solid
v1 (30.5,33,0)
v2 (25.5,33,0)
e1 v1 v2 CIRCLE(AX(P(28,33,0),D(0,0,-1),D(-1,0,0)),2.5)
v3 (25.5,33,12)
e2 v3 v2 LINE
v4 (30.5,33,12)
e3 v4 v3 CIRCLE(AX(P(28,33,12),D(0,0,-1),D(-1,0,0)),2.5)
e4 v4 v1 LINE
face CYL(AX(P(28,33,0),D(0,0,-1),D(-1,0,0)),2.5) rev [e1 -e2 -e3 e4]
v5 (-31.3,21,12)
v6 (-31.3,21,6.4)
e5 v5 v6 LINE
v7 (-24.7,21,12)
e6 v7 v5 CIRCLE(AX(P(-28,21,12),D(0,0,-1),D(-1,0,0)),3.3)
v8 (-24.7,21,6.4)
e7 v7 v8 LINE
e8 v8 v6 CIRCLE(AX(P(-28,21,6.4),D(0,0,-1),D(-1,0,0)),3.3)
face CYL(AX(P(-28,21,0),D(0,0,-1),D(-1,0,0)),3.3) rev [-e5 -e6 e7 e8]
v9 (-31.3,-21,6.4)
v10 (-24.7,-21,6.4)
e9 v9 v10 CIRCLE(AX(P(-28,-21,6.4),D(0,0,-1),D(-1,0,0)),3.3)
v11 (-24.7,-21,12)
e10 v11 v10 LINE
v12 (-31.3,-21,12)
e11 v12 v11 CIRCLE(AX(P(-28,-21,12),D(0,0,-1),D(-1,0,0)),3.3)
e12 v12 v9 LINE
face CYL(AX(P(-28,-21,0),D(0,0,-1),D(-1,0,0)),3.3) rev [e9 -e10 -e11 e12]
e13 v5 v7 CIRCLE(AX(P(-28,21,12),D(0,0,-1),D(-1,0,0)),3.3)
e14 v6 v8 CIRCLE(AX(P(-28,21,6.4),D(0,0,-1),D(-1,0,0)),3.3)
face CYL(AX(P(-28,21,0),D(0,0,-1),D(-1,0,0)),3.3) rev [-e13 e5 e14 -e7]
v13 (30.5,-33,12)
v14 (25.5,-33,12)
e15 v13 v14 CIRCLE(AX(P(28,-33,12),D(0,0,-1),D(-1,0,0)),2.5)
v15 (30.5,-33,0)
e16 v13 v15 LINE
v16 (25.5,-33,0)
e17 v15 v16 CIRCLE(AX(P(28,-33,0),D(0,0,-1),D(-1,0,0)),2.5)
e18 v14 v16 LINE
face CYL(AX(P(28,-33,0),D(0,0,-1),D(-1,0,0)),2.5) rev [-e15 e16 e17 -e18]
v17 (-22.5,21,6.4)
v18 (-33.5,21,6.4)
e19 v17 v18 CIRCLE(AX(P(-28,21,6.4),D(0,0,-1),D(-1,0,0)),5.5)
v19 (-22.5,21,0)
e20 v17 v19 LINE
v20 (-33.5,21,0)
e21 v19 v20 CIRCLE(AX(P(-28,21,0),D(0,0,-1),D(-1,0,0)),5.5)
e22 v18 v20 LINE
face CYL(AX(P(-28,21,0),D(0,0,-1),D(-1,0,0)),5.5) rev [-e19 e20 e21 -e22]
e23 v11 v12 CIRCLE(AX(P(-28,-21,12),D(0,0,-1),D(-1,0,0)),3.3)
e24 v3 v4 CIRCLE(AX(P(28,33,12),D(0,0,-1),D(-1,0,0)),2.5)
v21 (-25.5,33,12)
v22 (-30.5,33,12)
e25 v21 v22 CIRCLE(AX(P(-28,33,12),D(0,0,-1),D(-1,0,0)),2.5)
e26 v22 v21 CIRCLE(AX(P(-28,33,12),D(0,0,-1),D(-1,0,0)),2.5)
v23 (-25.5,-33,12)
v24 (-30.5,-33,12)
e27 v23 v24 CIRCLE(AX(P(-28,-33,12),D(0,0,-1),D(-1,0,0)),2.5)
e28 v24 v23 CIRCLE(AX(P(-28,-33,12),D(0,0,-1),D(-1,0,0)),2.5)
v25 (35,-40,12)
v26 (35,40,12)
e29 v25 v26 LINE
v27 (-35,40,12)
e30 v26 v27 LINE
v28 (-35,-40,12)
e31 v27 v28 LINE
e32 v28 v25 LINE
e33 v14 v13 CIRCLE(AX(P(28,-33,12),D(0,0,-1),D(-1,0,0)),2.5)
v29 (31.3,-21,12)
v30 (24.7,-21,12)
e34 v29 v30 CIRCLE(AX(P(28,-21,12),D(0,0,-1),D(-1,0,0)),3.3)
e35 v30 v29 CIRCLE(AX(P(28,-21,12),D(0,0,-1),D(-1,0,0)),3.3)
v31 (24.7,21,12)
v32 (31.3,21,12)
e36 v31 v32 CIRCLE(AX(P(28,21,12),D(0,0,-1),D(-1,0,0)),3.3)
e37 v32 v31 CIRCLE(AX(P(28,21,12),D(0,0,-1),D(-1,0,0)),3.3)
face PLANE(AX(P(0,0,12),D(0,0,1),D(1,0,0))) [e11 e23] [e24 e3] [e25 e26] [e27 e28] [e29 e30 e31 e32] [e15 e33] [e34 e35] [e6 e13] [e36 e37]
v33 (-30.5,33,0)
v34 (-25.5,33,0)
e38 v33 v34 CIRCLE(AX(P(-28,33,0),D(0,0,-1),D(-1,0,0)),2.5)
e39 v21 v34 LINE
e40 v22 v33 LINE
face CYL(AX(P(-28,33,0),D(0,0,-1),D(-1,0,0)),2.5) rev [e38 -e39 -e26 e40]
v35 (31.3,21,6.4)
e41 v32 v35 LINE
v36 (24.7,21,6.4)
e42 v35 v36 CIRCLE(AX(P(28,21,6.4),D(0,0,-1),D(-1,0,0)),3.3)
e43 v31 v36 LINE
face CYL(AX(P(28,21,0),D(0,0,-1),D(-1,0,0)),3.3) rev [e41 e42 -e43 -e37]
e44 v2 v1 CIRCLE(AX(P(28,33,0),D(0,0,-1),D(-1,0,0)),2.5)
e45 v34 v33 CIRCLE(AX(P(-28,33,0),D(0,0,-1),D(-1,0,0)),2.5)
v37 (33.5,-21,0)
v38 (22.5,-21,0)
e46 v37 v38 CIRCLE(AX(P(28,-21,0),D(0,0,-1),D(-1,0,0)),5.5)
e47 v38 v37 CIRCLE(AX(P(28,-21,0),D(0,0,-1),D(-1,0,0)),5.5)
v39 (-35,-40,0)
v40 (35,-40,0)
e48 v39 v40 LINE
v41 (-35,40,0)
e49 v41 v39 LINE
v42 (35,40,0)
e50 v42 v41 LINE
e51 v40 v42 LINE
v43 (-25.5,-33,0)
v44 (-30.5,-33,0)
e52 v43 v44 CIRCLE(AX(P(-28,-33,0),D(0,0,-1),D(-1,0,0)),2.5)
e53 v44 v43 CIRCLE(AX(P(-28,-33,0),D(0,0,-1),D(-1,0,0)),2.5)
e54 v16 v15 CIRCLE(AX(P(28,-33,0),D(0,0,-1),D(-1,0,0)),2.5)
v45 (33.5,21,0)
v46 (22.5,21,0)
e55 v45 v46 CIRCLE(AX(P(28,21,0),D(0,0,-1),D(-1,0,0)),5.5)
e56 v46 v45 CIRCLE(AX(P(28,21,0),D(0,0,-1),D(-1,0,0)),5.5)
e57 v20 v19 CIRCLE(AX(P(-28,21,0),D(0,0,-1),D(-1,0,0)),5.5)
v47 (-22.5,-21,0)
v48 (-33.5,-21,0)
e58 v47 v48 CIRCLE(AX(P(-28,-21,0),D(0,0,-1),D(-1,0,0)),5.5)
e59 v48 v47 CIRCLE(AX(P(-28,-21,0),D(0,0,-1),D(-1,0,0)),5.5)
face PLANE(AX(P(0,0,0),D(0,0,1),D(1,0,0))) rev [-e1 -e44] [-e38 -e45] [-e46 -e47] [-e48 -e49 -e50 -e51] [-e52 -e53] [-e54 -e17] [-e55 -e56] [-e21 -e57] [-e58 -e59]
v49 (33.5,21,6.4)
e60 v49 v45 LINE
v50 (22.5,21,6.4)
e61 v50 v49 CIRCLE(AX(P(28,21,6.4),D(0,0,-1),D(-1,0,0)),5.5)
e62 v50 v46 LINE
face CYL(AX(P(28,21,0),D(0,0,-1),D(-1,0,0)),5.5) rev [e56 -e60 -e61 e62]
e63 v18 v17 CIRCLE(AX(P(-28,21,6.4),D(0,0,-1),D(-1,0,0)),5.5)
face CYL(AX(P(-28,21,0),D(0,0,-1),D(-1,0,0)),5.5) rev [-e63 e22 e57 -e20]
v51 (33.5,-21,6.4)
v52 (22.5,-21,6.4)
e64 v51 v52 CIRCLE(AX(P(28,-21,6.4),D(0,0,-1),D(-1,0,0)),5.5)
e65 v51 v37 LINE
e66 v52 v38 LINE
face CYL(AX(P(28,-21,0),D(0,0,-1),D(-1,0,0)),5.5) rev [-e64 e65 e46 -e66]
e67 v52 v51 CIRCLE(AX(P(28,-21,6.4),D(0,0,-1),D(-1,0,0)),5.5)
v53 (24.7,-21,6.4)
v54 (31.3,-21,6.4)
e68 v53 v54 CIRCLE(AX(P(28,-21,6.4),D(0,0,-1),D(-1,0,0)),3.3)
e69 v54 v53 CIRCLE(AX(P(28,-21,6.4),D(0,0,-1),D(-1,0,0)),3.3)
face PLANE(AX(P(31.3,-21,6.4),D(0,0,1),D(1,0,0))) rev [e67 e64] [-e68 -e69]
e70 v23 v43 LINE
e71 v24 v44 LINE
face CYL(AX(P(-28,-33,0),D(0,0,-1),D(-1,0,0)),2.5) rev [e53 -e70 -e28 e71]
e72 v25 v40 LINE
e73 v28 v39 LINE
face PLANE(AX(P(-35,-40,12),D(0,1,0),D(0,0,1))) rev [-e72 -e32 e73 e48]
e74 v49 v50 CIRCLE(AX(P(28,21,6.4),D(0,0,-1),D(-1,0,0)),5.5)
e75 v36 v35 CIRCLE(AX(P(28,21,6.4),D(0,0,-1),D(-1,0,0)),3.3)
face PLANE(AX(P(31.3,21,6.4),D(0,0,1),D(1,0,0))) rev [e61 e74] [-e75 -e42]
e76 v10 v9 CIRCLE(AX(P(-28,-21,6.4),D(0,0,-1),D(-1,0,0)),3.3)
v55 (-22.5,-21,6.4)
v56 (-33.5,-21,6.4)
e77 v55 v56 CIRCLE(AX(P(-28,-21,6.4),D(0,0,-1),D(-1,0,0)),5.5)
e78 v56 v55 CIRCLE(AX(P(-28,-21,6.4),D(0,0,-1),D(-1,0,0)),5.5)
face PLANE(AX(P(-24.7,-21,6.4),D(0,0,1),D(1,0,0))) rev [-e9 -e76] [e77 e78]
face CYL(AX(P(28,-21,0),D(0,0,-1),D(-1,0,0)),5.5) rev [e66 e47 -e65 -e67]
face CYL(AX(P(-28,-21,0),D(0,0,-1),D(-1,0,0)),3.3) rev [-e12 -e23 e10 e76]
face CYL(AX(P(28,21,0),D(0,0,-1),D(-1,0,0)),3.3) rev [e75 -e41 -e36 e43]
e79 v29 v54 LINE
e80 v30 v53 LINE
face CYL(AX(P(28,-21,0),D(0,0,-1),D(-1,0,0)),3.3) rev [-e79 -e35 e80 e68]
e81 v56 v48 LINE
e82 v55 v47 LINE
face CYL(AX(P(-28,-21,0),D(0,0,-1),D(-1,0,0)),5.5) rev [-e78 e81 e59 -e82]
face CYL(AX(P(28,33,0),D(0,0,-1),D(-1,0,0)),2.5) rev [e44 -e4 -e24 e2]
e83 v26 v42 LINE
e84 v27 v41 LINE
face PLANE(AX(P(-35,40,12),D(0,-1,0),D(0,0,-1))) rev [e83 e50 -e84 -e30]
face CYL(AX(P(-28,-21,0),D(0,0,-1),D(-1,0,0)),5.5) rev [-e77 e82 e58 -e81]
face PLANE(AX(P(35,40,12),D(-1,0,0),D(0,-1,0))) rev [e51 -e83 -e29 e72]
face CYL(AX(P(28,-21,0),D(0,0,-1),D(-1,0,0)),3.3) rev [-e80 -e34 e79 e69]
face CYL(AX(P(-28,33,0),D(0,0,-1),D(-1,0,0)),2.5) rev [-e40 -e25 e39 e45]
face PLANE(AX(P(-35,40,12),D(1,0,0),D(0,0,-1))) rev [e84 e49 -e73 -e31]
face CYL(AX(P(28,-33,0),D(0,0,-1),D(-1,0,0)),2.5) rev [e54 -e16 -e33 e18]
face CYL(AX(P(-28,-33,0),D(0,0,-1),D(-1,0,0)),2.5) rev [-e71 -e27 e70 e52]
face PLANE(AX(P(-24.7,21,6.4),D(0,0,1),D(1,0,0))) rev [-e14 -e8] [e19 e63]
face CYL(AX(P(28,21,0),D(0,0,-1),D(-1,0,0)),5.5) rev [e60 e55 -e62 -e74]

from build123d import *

# Parameters (mm, degrees)
SKETCH_1_W                     = 70
SKETCH_1_H                     = 80
EXTRUDE_1_DEPTH                = 12
HOLE_WIZARD_M6_1_D             = 5
HOLE_WIZARD_M6_1_2_D           = 6.6
HOLE_WIZARD_M6_1_2_CBORE_D     = 11
HOLE_WIZARD_M6_1_2_CBORE_DEPTH = 6.4


with BuildPart() as part:
    # 草图1 → 凸台-拉伸1 (new body)
    with BuildSketch(Plane.XY):
        Rectangle(SKETCH_1_W, SKETCH_1_H)
    extrude(amount=EXTRUDE_1_DEPTH)

    # Hole Wizard M6 _1 (through all)
    with Locations(Plane(origin=(0, 0, 0), x_dir=(-1, 0, 0), z_dir=(0, 0, -1))):
        with Locations((28, 33), (28, -33), (-28, -33), (-28, 33)):
            Hole(HOLE_WIZARD_M6_1_D / 2)

    # Hole Wizard M6 _1 2 (through all)
    with Locations(Plane(origin=(0, 0, 0), x_dir=(-1, 0, 0), z_dir=(0, 0, -1))):
        with Locations((-28, -21), (-28, 21), (28, -21), (28, 21)):
            CounterBoreHole(HOLE_WIZARD_M6_1_2_D / 2, HOLE_WIZARD_M6_1_2_CBORE_D / 2, HOLE_WIZARD_M6_1_2_CBORE_DEPTH)


solid = part.part
